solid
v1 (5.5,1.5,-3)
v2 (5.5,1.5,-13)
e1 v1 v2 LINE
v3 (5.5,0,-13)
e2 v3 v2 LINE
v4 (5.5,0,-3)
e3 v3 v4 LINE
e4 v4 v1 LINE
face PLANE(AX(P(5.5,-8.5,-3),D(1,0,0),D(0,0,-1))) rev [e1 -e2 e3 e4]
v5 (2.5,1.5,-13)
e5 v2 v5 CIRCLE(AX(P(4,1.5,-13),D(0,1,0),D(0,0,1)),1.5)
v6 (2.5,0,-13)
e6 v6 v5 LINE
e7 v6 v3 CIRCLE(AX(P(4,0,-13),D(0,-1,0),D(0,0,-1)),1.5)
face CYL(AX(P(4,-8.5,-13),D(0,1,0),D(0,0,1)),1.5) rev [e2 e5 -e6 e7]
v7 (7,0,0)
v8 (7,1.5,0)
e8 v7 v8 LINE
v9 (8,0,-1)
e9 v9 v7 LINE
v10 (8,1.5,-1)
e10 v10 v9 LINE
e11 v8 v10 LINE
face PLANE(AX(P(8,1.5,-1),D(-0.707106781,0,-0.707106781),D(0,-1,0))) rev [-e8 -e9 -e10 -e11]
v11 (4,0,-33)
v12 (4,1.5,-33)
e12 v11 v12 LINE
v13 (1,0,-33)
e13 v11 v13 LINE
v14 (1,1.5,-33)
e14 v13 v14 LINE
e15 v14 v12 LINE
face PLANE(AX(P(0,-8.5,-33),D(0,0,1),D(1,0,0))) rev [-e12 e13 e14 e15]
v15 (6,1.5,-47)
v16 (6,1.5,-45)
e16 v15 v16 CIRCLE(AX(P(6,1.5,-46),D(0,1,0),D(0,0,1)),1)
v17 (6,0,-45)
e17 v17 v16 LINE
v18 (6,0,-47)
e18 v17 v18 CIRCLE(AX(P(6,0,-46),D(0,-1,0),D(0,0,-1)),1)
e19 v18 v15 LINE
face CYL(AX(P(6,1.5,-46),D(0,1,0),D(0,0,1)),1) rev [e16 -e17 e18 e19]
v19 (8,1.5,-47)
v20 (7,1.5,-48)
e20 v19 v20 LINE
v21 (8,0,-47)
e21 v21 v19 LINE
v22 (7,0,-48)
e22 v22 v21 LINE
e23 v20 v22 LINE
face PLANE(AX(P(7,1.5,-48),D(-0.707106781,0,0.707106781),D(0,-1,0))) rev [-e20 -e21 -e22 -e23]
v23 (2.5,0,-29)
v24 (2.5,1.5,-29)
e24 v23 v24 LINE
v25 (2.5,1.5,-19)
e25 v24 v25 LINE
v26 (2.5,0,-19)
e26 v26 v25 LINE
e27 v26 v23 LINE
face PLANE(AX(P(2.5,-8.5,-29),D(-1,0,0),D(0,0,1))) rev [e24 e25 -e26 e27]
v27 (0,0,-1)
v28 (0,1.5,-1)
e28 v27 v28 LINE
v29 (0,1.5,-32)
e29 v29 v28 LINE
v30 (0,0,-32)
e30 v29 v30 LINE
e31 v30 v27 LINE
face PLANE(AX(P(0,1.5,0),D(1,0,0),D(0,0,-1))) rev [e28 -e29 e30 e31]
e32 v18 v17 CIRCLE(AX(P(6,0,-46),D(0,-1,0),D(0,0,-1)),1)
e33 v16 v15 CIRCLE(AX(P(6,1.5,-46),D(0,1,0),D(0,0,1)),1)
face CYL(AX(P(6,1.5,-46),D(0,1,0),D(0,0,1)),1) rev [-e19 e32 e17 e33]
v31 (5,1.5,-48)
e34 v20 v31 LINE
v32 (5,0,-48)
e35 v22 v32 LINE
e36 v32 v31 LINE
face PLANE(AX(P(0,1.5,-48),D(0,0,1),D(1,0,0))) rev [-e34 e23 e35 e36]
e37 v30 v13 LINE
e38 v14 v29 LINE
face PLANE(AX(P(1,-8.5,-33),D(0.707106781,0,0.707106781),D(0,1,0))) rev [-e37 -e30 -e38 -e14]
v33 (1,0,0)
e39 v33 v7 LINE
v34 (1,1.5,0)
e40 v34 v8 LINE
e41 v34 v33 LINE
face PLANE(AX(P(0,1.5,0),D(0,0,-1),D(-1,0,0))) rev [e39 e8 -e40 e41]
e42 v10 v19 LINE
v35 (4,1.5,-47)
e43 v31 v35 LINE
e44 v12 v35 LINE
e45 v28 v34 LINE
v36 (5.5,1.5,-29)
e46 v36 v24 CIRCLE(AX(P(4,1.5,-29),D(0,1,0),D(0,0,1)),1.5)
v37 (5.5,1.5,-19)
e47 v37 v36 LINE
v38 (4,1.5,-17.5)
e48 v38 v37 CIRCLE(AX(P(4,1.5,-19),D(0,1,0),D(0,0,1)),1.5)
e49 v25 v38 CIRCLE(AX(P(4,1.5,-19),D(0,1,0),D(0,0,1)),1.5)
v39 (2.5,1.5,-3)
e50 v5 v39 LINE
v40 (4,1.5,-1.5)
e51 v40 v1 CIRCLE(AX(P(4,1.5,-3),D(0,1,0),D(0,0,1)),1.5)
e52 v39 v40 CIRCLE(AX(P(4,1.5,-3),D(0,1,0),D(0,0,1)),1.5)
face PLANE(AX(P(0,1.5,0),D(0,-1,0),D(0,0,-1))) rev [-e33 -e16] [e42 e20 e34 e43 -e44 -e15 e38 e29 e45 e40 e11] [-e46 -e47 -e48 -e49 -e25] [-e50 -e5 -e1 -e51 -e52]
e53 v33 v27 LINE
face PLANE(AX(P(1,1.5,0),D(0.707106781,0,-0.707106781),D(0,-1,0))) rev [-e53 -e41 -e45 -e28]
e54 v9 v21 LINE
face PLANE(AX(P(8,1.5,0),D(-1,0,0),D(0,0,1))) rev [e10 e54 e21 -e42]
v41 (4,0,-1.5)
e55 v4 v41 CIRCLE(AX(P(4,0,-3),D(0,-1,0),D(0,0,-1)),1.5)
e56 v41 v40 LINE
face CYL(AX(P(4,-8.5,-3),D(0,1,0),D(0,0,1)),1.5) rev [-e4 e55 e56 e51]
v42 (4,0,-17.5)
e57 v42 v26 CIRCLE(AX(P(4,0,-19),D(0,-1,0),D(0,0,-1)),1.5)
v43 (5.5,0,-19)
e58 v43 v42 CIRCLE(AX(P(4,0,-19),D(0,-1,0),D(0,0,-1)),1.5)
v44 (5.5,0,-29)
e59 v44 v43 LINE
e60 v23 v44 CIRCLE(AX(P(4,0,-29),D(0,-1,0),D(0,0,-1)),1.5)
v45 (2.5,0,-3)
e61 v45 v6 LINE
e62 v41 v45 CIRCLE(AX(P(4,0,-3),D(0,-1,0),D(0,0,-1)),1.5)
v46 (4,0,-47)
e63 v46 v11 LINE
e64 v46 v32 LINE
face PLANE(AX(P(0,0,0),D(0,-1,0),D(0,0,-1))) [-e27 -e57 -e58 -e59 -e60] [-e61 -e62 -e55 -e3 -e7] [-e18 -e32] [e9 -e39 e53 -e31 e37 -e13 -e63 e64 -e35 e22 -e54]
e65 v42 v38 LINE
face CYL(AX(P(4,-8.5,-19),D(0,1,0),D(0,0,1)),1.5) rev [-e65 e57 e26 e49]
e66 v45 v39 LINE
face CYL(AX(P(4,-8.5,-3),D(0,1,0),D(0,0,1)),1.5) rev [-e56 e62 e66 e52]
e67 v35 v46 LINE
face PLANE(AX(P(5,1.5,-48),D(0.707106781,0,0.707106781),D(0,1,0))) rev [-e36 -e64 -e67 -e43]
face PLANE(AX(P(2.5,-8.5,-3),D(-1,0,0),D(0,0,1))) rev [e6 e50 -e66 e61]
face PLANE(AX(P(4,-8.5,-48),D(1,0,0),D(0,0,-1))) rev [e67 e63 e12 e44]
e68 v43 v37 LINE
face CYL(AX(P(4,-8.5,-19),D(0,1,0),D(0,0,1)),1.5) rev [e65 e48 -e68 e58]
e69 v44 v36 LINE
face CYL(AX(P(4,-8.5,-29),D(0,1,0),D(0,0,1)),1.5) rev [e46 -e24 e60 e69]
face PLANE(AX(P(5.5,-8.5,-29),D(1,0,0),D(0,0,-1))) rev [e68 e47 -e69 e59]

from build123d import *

# Parameters (mm, degrees)
SKETCH1_W                      = 8
SKETCH1_H                      = 48
BOSS_EXTRUDE1_DEPTH            = 1.5
F_2_5_2_5_DIAMETER_HOLE1_D     = 2
F_2_5_2_5_DIAMETER_HOLE1_DEPTH = 5
F_2_5_2_5_DIAMETER_HOLE1_TIP   = 0.600860619
SKETCH6_W                      = 4
SKETCH6_H                      = 15
CUT_EXTRUDE1_DEPTH             = 10
SKETCH7_R                      = 1.5
CUT_EXTRUDE2_DEPTH             = 10
CHAMFER1_SIZE                  = 1
CUT_EXTRUDE3_DEPTH             = 10


with BuildPart() as part:
    # Sketch1 → Boss-Extrude1 (new body)
    with BuildSketch(Plane(origin=(0, 0, 0), x_dir=(1, 0, 0), z_dir=(0, 1, 0))):
        with Locations((4, 24)):
            Rectangle(SKETCH1_W, SKETCH1_H)
    extrude(amount=BOSS_EXTRUDE1_DEPTH)

    # Ø2.5 (2.5) Diameter Hole1
    with Locations(Plane(origin=(0, 1.5, 0), x_dir=(1, 0, 0), z_dir=(0, 1, 0))):
        with Locations((6, 46)):
            Hole(F_2_5_2_5_DIAMETER_HOLE1_D / 2, depth=F_2_5_2_5_DIAMETER_HOLE1_DEPTH)
            with Locations((0, 0, -(F_2_5_2_5_DIAMETER_HOLE1_DEPTH + F_2_5_2_5_DIAMETER_HOLE1_TIP / 2))):  # 118° drill point
                Cone(0, F_2_5_2_5_DIAMETER_HOLE1_D / 2, F_2_5_2_5_DIAMETER_HOLE1_TIP, mode=Mode.SUBTRACT)

    # Sketch6 → Cut-Extrude1 (cut)
    with BuildSketch(Plane(origin=(0, 1.5, 0), x_dir=(1, 0, 0), z_dir=(0, 1, 0))):
        with Locations((2, 40.5)):
            Rectangle(SKETCH6_W, SKETCH6_H)
    extrude(amount=-CUT_EXTRUDE1_DEPTH, mode=Mode.SUBTRACT)

    # Sketch7 → Cut-Extrude2 (cut)
    with BuildSketch(Plane(origin=(0, 1.5, 0), x_dir=(1, 0, 0), z_dir=(0, 1, 0))):
        with Locations(Location((4, 24, 0), (0, 0, 270))):
            Circle(SKETCH7_R)
        with Locations(Location((4, 8, 0), (0, 0, 270))):
            Circle(SKETCH7_R)
    extrude(amount=-CUT_EXTRUDE2_DEPTH, mode=Mode.SUBTRACT)

    # Chamfer1
    chamfer1_edges = [part.edges().sort_by_distance(p)[0] for p in [
        (0, 0.75, -33),
        (4, 0.75, -48),
        (8, 0.75, -48),
        (8, 0.75, 0),
        (0, 0.75, 0),
    ]]
    chamfer(chamfer1_edges, length=CHAMFER1_SIZE)

    # Sketch8 → Cut-Extrude3 (cut)
    with BuildSketch(Plane(origin=(0, 1.5, 0), x_dir=(1, 0, 0), z_dir=(0, 1, 0))):
        with BuildLine():
            Line((5.5, 29), (5.5, 19))
            ThreePointArc((5.5, 19), (4, 17.5), (2.5, 19))
            Line((2.5, 19), (2.5, 29))
            ThreePointArc((2.5, 29), (4, 30.5), (5.5, 29))
        make_face()
        with BuildLine():
            Line((2.5, 3), (2.5, 13))
            ThreePointArc((2.5, 13), (4, 14.5), (5.5, 13))
            Line((5.5, 13), (5.5, 3))
            ThreePointArc((5.5, 3), (4, 1.5), (2.5, 3))
        make_face()
    extrude(amount=-CUT_EXTRUDE3_DEPTH, mode=Mode.SUBTRACT)


solid = part.part
